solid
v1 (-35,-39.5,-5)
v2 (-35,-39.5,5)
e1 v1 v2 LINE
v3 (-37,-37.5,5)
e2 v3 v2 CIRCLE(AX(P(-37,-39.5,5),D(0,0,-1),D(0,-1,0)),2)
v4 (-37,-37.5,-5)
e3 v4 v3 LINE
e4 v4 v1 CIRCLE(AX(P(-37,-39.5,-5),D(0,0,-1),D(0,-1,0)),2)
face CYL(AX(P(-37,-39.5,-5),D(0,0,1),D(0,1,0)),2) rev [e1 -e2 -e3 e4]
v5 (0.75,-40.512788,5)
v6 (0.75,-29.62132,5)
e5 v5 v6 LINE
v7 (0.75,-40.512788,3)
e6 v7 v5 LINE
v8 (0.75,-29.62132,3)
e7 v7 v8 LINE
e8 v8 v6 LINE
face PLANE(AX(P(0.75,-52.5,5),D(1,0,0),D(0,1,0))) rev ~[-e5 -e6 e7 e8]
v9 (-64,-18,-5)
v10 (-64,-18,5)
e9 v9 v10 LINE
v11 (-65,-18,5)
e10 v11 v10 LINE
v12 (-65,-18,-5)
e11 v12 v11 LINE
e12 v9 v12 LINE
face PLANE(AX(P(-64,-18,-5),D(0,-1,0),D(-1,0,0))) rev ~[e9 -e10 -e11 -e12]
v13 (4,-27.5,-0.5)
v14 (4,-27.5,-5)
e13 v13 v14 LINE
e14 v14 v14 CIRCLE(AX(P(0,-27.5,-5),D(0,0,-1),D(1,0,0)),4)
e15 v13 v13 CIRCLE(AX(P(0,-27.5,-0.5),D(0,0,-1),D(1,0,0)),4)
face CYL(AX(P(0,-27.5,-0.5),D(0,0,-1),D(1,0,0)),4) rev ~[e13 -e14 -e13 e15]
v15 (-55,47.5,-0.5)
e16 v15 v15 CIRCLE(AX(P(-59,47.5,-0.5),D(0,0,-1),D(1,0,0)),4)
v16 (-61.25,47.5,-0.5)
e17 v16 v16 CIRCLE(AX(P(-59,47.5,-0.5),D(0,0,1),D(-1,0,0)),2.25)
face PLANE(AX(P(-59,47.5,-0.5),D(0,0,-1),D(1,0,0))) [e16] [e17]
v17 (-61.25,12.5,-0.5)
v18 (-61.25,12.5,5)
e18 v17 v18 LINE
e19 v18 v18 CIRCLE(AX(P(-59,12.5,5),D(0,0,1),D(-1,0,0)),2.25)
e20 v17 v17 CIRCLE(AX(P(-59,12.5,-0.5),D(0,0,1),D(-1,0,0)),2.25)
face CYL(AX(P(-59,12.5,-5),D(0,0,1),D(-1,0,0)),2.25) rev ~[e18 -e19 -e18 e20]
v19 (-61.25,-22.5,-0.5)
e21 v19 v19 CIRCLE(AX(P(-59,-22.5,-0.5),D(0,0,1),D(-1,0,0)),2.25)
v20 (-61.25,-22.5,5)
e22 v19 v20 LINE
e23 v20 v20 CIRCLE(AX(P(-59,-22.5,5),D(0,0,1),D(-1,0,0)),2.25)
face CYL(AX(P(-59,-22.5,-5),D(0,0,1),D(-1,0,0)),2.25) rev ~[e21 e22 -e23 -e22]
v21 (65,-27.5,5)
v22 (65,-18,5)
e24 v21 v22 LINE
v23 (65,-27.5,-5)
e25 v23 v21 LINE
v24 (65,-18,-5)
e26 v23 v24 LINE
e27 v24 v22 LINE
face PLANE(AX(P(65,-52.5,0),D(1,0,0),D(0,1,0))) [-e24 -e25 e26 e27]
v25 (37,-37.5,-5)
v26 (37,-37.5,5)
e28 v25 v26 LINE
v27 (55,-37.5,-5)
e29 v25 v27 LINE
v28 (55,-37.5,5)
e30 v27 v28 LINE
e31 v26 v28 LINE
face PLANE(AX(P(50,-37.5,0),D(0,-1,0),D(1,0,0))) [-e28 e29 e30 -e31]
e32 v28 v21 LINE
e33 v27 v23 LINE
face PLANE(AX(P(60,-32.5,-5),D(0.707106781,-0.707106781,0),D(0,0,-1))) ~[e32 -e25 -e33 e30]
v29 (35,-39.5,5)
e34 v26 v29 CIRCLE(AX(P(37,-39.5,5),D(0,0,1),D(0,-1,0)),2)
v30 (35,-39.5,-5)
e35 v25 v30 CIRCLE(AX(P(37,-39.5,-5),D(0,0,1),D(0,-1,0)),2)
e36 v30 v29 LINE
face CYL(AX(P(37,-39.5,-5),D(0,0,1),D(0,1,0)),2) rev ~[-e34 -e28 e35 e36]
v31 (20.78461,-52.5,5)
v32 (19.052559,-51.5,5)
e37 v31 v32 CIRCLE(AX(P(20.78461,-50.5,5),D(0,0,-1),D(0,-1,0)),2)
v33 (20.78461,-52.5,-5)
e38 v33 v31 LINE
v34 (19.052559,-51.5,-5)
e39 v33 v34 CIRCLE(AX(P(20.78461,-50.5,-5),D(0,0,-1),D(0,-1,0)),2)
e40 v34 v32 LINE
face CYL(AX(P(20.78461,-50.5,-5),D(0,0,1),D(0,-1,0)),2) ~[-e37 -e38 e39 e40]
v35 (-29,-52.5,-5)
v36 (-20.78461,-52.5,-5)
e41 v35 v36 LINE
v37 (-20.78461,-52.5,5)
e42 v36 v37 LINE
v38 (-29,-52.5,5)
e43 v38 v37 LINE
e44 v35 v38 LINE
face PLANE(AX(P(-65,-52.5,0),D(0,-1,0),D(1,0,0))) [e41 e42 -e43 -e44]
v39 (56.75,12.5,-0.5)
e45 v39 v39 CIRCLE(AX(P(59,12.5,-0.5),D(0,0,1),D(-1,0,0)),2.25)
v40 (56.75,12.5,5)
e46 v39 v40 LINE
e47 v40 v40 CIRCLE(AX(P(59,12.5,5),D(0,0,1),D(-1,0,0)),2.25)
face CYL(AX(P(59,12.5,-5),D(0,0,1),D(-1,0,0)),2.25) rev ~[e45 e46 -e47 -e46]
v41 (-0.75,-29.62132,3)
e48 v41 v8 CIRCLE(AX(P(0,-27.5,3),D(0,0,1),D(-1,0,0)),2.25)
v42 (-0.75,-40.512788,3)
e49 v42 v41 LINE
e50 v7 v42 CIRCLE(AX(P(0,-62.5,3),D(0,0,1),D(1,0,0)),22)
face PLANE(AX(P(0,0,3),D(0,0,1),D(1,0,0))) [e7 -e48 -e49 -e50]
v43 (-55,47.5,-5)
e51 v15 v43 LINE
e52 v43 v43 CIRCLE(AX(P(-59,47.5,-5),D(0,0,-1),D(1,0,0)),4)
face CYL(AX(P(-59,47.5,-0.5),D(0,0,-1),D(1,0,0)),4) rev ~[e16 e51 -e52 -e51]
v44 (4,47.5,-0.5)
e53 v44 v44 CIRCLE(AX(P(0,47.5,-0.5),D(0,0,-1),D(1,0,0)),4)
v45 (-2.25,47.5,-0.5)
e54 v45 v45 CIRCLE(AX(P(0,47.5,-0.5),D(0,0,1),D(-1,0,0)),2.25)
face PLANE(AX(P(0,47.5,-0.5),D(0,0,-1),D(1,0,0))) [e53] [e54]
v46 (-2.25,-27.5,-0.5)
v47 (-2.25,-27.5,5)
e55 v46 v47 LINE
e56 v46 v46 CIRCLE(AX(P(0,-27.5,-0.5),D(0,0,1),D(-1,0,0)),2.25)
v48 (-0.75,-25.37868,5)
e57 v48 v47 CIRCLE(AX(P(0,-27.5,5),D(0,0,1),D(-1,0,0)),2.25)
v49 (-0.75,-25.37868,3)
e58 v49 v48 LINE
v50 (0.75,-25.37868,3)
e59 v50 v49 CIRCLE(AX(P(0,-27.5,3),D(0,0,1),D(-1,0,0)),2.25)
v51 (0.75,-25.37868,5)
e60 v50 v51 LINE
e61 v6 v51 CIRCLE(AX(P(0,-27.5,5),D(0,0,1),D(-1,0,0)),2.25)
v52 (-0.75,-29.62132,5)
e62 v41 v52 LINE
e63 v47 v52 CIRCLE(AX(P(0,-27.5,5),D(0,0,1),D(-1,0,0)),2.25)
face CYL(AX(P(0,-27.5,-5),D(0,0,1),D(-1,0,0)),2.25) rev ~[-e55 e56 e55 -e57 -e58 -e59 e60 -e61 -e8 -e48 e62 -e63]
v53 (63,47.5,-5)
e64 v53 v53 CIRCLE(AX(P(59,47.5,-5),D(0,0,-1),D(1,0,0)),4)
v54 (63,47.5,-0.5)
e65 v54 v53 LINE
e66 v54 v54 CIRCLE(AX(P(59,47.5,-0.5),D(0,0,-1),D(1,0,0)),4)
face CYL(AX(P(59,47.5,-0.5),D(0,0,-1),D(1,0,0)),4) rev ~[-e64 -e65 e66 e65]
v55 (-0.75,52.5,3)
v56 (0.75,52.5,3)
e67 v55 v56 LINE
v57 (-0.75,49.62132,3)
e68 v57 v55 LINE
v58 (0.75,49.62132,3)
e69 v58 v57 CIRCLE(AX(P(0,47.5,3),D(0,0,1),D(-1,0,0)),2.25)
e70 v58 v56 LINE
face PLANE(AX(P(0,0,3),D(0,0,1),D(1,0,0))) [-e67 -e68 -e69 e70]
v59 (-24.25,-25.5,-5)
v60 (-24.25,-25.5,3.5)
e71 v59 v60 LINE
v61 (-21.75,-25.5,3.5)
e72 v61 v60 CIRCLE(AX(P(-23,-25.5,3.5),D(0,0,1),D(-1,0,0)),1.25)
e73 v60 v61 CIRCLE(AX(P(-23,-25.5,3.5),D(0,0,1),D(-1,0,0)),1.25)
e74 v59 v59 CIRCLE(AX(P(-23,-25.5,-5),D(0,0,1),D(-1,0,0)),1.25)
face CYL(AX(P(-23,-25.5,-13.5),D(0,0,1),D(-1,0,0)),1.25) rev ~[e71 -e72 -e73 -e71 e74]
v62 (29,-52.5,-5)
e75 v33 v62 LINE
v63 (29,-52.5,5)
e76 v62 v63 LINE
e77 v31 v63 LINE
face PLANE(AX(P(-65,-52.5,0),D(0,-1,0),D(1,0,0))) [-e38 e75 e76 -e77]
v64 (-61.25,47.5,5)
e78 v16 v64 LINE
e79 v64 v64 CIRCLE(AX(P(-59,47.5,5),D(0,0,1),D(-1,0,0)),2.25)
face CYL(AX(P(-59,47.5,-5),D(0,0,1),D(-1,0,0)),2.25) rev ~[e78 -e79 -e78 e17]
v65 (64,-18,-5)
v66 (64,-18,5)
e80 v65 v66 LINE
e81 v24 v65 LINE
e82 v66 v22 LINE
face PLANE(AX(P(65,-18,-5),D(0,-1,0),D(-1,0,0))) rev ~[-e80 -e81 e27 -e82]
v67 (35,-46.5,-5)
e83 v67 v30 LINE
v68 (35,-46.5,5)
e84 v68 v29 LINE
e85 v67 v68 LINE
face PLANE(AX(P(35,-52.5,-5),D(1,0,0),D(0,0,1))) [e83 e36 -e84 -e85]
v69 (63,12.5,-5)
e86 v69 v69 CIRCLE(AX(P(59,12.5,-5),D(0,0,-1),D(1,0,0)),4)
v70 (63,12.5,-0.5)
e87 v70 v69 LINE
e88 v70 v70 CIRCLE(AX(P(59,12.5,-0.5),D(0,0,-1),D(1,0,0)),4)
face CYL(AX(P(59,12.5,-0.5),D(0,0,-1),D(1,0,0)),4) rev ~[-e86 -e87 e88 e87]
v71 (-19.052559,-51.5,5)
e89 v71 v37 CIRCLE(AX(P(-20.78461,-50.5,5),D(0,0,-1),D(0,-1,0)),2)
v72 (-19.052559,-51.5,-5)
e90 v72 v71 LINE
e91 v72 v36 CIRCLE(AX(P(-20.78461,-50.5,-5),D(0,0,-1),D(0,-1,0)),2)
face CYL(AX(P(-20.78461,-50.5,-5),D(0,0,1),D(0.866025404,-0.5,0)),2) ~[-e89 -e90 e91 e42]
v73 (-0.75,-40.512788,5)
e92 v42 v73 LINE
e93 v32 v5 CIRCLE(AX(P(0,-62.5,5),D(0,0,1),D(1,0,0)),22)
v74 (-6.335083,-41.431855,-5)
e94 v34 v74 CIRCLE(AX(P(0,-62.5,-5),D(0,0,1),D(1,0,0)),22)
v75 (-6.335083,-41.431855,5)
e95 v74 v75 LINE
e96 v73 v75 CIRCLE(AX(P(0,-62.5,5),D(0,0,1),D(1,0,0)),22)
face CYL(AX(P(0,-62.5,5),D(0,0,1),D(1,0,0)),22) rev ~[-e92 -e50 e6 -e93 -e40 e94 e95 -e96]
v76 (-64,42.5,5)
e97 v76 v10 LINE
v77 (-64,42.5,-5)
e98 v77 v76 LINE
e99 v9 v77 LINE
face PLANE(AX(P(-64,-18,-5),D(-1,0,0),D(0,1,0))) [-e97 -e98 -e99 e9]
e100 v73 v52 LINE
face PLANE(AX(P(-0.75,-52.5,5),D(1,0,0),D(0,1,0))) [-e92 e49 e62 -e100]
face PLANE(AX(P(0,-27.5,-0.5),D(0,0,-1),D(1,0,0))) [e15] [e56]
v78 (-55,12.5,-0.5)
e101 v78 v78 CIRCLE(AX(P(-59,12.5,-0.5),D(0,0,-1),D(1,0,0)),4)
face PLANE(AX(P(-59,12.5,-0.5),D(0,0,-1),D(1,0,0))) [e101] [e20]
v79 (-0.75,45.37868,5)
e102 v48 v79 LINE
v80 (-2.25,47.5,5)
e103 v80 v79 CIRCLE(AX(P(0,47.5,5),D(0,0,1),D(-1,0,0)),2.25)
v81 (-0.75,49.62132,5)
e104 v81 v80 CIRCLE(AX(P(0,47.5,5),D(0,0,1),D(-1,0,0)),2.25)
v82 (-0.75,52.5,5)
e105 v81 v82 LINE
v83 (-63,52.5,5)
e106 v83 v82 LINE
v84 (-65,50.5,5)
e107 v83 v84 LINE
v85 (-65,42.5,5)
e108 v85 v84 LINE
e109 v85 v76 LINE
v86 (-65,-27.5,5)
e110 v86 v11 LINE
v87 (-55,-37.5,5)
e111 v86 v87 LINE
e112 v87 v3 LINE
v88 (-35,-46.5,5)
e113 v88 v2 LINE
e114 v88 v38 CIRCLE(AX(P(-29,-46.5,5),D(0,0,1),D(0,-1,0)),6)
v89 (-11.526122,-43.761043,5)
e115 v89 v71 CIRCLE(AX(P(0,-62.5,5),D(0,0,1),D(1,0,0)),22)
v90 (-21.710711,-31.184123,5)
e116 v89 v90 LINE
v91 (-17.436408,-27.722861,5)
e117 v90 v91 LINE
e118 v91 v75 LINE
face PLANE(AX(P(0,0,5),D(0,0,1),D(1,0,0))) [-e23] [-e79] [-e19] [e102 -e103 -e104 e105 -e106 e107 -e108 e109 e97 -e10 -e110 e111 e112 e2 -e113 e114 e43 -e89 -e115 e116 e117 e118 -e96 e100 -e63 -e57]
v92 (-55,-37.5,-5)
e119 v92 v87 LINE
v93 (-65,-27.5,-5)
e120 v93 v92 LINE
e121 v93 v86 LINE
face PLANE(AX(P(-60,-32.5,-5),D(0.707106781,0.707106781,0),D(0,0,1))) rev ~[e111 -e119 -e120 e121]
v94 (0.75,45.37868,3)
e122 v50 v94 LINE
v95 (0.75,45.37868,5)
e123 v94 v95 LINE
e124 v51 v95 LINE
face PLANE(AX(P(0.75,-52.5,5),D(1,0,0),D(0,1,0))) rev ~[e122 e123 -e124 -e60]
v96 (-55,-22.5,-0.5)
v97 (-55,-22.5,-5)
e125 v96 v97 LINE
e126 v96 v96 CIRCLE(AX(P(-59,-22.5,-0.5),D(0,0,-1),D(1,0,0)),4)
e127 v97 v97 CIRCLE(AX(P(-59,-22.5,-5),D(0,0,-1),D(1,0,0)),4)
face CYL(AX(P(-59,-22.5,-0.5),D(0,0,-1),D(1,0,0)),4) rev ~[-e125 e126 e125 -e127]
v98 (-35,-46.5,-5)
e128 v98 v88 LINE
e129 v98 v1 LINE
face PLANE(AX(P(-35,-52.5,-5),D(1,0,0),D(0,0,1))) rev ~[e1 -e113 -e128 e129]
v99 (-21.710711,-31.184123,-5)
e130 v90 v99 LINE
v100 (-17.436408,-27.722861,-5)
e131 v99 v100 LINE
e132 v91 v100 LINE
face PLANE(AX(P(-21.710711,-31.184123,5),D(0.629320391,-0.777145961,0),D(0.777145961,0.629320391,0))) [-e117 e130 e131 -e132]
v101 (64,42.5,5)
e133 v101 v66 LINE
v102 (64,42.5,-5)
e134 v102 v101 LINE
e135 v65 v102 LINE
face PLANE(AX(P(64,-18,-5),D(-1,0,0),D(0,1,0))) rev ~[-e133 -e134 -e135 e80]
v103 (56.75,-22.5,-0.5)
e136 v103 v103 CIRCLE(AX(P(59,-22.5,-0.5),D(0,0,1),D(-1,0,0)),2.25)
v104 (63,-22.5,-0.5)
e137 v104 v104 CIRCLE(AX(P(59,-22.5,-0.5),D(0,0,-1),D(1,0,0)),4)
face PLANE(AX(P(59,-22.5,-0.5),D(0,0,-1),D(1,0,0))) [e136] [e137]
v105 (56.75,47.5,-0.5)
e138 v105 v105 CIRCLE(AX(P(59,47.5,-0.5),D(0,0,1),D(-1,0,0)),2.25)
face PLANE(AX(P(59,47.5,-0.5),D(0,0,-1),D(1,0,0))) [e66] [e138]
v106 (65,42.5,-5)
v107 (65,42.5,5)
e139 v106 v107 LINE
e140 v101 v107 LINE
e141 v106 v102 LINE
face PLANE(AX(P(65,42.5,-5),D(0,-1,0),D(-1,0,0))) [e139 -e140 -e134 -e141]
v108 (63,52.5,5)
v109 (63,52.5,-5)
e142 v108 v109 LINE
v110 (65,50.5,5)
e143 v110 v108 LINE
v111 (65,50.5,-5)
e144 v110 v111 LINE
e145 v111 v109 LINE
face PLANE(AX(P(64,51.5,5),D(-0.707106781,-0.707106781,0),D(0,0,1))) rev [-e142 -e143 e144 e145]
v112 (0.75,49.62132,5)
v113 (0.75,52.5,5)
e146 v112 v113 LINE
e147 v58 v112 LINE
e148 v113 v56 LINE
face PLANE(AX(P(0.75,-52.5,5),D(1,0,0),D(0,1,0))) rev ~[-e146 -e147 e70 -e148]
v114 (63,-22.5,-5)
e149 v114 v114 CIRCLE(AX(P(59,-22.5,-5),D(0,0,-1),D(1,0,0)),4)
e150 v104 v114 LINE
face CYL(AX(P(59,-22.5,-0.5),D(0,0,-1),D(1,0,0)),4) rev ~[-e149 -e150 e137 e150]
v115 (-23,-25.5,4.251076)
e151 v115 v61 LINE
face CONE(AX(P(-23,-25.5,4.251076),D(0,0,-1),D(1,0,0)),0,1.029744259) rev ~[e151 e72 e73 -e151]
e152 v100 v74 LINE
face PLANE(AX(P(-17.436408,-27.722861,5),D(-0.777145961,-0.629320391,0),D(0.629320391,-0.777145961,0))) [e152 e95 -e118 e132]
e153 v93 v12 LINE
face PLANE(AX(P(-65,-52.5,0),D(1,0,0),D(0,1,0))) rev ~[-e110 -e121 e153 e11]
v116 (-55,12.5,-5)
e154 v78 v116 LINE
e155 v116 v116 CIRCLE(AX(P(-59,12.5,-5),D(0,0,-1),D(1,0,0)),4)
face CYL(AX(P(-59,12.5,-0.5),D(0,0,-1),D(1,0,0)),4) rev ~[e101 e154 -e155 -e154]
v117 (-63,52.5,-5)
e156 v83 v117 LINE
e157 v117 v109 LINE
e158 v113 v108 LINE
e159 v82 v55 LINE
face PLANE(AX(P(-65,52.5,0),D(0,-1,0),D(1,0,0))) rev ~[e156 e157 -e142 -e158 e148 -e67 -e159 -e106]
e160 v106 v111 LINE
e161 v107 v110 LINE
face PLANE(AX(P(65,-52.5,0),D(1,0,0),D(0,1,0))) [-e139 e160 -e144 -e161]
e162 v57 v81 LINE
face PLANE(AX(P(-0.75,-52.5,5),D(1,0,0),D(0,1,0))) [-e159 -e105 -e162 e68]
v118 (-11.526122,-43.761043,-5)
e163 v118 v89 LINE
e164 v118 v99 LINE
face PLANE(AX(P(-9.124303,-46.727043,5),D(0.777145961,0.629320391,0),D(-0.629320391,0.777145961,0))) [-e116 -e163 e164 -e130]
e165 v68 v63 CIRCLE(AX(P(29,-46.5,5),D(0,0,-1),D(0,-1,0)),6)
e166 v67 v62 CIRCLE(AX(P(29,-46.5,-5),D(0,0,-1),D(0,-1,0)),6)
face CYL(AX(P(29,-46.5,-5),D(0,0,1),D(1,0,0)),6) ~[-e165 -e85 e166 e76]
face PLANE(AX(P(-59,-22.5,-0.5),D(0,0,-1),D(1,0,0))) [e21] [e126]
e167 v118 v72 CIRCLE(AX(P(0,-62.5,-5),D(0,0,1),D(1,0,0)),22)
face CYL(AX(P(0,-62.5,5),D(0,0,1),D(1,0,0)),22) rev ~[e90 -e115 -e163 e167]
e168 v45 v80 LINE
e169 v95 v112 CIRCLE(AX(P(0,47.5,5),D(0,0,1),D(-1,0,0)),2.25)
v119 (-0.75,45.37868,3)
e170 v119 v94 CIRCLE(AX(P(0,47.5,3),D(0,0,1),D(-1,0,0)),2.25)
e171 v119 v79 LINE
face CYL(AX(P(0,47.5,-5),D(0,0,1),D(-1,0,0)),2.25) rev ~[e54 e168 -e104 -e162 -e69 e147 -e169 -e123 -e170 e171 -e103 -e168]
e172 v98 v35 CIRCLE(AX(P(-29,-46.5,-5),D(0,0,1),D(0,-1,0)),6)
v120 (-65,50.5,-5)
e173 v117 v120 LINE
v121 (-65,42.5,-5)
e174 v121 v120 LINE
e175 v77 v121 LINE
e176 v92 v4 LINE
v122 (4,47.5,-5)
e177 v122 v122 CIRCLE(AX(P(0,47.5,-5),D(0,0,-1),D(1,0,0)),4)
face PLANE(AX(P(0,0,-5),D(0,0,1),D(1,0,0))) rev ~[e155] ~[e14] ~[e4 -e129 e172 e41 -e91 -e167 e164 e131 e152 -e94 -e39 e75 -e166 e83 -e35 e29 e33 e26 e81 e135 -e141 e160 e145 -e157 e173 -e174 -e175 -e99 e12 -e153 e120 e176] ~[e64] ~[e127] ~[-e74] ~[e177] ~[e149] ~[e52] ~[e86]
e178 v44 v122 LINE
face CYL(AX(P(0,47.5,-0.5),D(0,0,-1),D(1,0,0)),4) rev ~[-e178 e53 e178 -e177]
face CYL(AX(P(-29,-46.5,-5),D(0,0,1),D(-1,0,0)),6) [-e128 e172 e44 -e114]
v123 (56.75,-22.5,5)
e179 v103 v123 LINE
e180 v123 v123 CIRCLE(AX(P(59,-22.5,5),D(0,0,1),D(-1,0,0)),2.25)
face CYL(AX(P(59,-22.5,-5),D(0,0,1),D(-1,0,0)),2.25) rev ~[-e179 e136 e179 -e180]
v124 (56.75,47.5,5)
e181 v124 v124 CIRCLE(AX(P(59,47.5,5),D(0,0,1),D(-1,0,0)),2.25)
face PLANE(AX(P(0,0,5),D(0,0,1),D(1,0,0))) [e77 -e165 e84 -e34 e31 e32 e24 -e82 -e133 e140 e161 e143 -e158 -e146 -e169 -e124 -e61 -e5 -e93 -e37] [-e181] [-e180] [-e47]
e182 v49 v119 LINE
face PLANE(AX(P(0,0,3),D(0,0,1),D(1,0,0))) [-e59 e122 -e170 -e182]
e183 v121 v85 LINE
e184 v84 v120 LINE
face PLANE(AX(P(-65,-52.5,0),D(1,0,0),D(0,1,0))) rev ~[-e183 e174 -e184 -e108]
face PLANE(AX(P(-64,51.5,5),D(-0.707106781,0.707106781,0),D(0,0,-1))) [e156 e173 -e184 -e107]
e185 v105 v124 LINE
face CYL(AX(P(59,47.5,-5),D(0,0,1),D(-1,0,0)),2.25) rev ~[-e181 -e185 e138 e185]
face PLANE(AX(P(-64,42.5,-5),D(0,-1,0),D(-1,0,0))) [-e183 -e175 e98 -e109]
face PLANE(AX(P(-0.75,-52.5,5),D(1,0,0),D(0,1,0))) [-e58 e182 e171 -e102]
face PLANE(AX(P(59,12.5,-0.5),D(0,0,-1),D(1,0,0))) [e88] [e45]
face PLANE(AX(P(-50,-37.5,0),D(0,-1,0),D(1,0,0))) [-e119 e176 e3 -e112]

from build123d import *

# Parameters (mm, degrees)
SKETCH1_W                                            = 130
SKETCH1_H                                            = 105
BOSS_EXTRUDE1_DEPTH                                  = 5
SKETCH3_R                                            = 22
CUT_EXTRUDE2_DEPTH                                   = 85.150163399
SKETCH7_W                                            = 30
SKETCH7_H                                            = 10
CUT_EXTRUDE5_DEPTH                                   = 15
FILLET1_R                                            = 6
CHAMFER1_SIZE                                        = 10
FILLET2_R                                            = 2
CUT_EXTRUDE8_DEPTH                                   = 85.150163399
FILLET3_R                                            = 2
CHAMFER2_SIZE                                        = 2
SKETCH15_W                                           = 1
SKETCH15_H                                           = 60.5
CUT_EXTRUDE10_DEPTH                                  = 85.150163399
HOLE_SIZE_PER_SOCKET_HEAD_CAP_SCREW_TYPE_D           = 4.5
HOLE_SIZE_PER_SOCKET_HEAD_CAP_SCREW_TYPE_CBORE_D     = 8
HOLE_SIZE_PER_SOCKET_HEAD_CAP_SCREW_TYPE_CBORE_DEPTH = 4.5
M3_TAPPED_HOLE1_D                                    = 2.5
M3_TAPPED_HOLE1_DEPTH                                = 8.5
M3_TAPPED_HOLE1_TIP                                  = 0.751075774
SKETCH20_W                                           = 1.5
SKETCH20_H                                           = 105
CUT_EXTRUDE11_DEPTH                                  = 2


with BuildPart() as part:
    # Sketch1 → Boss-Extrude1 (new, symmetric)
    with BuildSketch(Plane.XY):
        Rectangle(SKETCH1_W, SKETCH1_H)
    extrude(amount=BOSS_EXTRUDE1_DEPTH, both=True)

    # Sketch3 → Cut-Extrude2 (cut, through all)
    with BuildSketch(Plane.XY.offset(5)):
        with Locations((0, -62.5)):
            Circle(SKETCH3_R)
    extrude(amount=-CUT_EXTRUDE2_DEPTH, mode=Mode.SUBTRACT)

    # Sketch7 → Cut-Extrude5 (cut)
    with BuildSketch(Plane.XZ.offset(52.5)):
        with Locations((-50, 0)):
            Rectangle(SKETCH7_W, SKETCH7_H)
        with Locations((50, 0)):
            Rectangle(SKETCH7_W, SKETCH7_H)
    extrude(amount=-CUT_EXTRUDE5_DEPTH, mode=Mode.SUBTRACT)

    # Fillet1
    fillet1_edges = [part.edges().sort_by_distance(p)[0] for p in [
        (-35, -52.5, 0),
        (35, -52.5, 0),
    ]]
    fillet(fillet1_edges, radius=FILLET1_R)

    # Chamfer1
    chamfer1_edges = [part.edges().sort_by_distance(p)[0] for p in [
        (-65, -37.5, 0),
        (65, -37.5, 0),
    ]]
    chamfer(chamfer1_edges, length=CHAMFER1_SIZE)

    # Fillet2
    fillet2_edges = [part.edges().sort_by_distance(p)[0] for p in [
        (-35, -37.5, 0),
        (35, -37.5, 0),
    ]]
    fillet(fillet2_edges, radius=FILLET2_R)

    # Sketch10 → Cut-Extrude8 (cut, through all)
    with BuildSketch(Plane.XY.offset(5)):
        Polygon((-21.710710609, -31.184123297), (-17.436407821, -27.722861146), (-4.85, -43.265780375), (-9.124302788, -46.727042526), align=None)
    extrude(amount=-CUT_EXTRUDE8_DEPTH, mode=Mode.SUBTRACT)

    # Fillet3
    fillet3_edges = [part.edges().sort_by_distance(p)[0] for p in [
        (-19.595917942, -52.5, 0),
        (19.595917942, -52.5, 0),
    ]]
    fillet(fillet3_edges, radius=FILLET3_R)

    # Chamfer2
    chamfer2_edges = [part.edges().sort_by_distance(p)[0] for p in [
        (-65, 52.5, 0),
        (65, 52.5, 0),
    ]]
    chamfer(chamfer2_edges, length=CHAMFER2_SIZE)

    # Sketch15 → Cut-Extrude10 (cut, through all)
    with BuildSketch(Plane(origin=(0, 0, -5), x_dir=(-1, 0, 0), z_dir=(0, 0, -1))):
        with Locations((-64.5, 12.25)):
            Rectangle(SKETCH15_W, SKETCH15_H)
        with Locations((64.5, 12.25)):
            Rectangle(SKETCH15_W, SKETCH15_H)
    extrude(amount=-CUT_EXTRUDE10_DEPTH, mode=Mode.SUBTRACT)

    # Hole size per socket head cap screw type 0 (through all)
    with Locations(Plane(origin=(-18.523886338, 13.049633662, -5), x_dir=(1, 0, 0), z_dir=(0, 0, -1))):
        with Locations((77.523886338, -34.450366338), (18.523886338, -34.450366338), (-40.476113662, -34.450366338), (-40.476113662, 0.549633662), (-40.476113662, 35.549633662), (18.523886338, 40.549633662), (77.523886338, 35.549633662), (77.523886338, 0.549633662)):
            CounterBoreHole(HOLE_SIZE_PER_SOCKET_HEAD_CAP_SCREW_TYPE_D / 2, HOLE_SIZE_PER_SOCKET_HEAD_CAP_SCREW_TYPE_CBORE_D / 2, HOLE_SIZE_PER_SOCKET_HEAD_CAP_SCREW_TYPE_CBORE_DEPTH)

    # M3 Tapped Hole1
    with Locations(Plane(origin=(-15.568631127, 3.135719595, -5), x_dir=(1, 0, 0), z_dir=(0, 0, -1))):
        with Locations((-7.431368873, 28.635719595)):
            Hole(M3_TAPPED_HOLE1_D / 2, depth=M3_TAPPED_HOLE1_DEPTH)
            with Locations((0, 0, -(M3_TAPPED_HOLE1_DEPTH + M3_TAPPED_HOLE1_TIP / 2))):  # 118° drill point
                Cone(0, M3_TAPPED_HOLE1_D / 2, M3_TAPPED_HOLE1_TIP, mode=Mode.SUBTRACT)

    # Sketch20 → Cut-Extrude11 (cut)
    with BuildSketch(Plane.XY.offset(5)):
        Rectangle(SKETCH20_W, SKETCH20_H)
    extrude(amount=-CUT_EXTRUDE11_DEPTH, mode=Mode.SUBTRACT)


solid = part.part
